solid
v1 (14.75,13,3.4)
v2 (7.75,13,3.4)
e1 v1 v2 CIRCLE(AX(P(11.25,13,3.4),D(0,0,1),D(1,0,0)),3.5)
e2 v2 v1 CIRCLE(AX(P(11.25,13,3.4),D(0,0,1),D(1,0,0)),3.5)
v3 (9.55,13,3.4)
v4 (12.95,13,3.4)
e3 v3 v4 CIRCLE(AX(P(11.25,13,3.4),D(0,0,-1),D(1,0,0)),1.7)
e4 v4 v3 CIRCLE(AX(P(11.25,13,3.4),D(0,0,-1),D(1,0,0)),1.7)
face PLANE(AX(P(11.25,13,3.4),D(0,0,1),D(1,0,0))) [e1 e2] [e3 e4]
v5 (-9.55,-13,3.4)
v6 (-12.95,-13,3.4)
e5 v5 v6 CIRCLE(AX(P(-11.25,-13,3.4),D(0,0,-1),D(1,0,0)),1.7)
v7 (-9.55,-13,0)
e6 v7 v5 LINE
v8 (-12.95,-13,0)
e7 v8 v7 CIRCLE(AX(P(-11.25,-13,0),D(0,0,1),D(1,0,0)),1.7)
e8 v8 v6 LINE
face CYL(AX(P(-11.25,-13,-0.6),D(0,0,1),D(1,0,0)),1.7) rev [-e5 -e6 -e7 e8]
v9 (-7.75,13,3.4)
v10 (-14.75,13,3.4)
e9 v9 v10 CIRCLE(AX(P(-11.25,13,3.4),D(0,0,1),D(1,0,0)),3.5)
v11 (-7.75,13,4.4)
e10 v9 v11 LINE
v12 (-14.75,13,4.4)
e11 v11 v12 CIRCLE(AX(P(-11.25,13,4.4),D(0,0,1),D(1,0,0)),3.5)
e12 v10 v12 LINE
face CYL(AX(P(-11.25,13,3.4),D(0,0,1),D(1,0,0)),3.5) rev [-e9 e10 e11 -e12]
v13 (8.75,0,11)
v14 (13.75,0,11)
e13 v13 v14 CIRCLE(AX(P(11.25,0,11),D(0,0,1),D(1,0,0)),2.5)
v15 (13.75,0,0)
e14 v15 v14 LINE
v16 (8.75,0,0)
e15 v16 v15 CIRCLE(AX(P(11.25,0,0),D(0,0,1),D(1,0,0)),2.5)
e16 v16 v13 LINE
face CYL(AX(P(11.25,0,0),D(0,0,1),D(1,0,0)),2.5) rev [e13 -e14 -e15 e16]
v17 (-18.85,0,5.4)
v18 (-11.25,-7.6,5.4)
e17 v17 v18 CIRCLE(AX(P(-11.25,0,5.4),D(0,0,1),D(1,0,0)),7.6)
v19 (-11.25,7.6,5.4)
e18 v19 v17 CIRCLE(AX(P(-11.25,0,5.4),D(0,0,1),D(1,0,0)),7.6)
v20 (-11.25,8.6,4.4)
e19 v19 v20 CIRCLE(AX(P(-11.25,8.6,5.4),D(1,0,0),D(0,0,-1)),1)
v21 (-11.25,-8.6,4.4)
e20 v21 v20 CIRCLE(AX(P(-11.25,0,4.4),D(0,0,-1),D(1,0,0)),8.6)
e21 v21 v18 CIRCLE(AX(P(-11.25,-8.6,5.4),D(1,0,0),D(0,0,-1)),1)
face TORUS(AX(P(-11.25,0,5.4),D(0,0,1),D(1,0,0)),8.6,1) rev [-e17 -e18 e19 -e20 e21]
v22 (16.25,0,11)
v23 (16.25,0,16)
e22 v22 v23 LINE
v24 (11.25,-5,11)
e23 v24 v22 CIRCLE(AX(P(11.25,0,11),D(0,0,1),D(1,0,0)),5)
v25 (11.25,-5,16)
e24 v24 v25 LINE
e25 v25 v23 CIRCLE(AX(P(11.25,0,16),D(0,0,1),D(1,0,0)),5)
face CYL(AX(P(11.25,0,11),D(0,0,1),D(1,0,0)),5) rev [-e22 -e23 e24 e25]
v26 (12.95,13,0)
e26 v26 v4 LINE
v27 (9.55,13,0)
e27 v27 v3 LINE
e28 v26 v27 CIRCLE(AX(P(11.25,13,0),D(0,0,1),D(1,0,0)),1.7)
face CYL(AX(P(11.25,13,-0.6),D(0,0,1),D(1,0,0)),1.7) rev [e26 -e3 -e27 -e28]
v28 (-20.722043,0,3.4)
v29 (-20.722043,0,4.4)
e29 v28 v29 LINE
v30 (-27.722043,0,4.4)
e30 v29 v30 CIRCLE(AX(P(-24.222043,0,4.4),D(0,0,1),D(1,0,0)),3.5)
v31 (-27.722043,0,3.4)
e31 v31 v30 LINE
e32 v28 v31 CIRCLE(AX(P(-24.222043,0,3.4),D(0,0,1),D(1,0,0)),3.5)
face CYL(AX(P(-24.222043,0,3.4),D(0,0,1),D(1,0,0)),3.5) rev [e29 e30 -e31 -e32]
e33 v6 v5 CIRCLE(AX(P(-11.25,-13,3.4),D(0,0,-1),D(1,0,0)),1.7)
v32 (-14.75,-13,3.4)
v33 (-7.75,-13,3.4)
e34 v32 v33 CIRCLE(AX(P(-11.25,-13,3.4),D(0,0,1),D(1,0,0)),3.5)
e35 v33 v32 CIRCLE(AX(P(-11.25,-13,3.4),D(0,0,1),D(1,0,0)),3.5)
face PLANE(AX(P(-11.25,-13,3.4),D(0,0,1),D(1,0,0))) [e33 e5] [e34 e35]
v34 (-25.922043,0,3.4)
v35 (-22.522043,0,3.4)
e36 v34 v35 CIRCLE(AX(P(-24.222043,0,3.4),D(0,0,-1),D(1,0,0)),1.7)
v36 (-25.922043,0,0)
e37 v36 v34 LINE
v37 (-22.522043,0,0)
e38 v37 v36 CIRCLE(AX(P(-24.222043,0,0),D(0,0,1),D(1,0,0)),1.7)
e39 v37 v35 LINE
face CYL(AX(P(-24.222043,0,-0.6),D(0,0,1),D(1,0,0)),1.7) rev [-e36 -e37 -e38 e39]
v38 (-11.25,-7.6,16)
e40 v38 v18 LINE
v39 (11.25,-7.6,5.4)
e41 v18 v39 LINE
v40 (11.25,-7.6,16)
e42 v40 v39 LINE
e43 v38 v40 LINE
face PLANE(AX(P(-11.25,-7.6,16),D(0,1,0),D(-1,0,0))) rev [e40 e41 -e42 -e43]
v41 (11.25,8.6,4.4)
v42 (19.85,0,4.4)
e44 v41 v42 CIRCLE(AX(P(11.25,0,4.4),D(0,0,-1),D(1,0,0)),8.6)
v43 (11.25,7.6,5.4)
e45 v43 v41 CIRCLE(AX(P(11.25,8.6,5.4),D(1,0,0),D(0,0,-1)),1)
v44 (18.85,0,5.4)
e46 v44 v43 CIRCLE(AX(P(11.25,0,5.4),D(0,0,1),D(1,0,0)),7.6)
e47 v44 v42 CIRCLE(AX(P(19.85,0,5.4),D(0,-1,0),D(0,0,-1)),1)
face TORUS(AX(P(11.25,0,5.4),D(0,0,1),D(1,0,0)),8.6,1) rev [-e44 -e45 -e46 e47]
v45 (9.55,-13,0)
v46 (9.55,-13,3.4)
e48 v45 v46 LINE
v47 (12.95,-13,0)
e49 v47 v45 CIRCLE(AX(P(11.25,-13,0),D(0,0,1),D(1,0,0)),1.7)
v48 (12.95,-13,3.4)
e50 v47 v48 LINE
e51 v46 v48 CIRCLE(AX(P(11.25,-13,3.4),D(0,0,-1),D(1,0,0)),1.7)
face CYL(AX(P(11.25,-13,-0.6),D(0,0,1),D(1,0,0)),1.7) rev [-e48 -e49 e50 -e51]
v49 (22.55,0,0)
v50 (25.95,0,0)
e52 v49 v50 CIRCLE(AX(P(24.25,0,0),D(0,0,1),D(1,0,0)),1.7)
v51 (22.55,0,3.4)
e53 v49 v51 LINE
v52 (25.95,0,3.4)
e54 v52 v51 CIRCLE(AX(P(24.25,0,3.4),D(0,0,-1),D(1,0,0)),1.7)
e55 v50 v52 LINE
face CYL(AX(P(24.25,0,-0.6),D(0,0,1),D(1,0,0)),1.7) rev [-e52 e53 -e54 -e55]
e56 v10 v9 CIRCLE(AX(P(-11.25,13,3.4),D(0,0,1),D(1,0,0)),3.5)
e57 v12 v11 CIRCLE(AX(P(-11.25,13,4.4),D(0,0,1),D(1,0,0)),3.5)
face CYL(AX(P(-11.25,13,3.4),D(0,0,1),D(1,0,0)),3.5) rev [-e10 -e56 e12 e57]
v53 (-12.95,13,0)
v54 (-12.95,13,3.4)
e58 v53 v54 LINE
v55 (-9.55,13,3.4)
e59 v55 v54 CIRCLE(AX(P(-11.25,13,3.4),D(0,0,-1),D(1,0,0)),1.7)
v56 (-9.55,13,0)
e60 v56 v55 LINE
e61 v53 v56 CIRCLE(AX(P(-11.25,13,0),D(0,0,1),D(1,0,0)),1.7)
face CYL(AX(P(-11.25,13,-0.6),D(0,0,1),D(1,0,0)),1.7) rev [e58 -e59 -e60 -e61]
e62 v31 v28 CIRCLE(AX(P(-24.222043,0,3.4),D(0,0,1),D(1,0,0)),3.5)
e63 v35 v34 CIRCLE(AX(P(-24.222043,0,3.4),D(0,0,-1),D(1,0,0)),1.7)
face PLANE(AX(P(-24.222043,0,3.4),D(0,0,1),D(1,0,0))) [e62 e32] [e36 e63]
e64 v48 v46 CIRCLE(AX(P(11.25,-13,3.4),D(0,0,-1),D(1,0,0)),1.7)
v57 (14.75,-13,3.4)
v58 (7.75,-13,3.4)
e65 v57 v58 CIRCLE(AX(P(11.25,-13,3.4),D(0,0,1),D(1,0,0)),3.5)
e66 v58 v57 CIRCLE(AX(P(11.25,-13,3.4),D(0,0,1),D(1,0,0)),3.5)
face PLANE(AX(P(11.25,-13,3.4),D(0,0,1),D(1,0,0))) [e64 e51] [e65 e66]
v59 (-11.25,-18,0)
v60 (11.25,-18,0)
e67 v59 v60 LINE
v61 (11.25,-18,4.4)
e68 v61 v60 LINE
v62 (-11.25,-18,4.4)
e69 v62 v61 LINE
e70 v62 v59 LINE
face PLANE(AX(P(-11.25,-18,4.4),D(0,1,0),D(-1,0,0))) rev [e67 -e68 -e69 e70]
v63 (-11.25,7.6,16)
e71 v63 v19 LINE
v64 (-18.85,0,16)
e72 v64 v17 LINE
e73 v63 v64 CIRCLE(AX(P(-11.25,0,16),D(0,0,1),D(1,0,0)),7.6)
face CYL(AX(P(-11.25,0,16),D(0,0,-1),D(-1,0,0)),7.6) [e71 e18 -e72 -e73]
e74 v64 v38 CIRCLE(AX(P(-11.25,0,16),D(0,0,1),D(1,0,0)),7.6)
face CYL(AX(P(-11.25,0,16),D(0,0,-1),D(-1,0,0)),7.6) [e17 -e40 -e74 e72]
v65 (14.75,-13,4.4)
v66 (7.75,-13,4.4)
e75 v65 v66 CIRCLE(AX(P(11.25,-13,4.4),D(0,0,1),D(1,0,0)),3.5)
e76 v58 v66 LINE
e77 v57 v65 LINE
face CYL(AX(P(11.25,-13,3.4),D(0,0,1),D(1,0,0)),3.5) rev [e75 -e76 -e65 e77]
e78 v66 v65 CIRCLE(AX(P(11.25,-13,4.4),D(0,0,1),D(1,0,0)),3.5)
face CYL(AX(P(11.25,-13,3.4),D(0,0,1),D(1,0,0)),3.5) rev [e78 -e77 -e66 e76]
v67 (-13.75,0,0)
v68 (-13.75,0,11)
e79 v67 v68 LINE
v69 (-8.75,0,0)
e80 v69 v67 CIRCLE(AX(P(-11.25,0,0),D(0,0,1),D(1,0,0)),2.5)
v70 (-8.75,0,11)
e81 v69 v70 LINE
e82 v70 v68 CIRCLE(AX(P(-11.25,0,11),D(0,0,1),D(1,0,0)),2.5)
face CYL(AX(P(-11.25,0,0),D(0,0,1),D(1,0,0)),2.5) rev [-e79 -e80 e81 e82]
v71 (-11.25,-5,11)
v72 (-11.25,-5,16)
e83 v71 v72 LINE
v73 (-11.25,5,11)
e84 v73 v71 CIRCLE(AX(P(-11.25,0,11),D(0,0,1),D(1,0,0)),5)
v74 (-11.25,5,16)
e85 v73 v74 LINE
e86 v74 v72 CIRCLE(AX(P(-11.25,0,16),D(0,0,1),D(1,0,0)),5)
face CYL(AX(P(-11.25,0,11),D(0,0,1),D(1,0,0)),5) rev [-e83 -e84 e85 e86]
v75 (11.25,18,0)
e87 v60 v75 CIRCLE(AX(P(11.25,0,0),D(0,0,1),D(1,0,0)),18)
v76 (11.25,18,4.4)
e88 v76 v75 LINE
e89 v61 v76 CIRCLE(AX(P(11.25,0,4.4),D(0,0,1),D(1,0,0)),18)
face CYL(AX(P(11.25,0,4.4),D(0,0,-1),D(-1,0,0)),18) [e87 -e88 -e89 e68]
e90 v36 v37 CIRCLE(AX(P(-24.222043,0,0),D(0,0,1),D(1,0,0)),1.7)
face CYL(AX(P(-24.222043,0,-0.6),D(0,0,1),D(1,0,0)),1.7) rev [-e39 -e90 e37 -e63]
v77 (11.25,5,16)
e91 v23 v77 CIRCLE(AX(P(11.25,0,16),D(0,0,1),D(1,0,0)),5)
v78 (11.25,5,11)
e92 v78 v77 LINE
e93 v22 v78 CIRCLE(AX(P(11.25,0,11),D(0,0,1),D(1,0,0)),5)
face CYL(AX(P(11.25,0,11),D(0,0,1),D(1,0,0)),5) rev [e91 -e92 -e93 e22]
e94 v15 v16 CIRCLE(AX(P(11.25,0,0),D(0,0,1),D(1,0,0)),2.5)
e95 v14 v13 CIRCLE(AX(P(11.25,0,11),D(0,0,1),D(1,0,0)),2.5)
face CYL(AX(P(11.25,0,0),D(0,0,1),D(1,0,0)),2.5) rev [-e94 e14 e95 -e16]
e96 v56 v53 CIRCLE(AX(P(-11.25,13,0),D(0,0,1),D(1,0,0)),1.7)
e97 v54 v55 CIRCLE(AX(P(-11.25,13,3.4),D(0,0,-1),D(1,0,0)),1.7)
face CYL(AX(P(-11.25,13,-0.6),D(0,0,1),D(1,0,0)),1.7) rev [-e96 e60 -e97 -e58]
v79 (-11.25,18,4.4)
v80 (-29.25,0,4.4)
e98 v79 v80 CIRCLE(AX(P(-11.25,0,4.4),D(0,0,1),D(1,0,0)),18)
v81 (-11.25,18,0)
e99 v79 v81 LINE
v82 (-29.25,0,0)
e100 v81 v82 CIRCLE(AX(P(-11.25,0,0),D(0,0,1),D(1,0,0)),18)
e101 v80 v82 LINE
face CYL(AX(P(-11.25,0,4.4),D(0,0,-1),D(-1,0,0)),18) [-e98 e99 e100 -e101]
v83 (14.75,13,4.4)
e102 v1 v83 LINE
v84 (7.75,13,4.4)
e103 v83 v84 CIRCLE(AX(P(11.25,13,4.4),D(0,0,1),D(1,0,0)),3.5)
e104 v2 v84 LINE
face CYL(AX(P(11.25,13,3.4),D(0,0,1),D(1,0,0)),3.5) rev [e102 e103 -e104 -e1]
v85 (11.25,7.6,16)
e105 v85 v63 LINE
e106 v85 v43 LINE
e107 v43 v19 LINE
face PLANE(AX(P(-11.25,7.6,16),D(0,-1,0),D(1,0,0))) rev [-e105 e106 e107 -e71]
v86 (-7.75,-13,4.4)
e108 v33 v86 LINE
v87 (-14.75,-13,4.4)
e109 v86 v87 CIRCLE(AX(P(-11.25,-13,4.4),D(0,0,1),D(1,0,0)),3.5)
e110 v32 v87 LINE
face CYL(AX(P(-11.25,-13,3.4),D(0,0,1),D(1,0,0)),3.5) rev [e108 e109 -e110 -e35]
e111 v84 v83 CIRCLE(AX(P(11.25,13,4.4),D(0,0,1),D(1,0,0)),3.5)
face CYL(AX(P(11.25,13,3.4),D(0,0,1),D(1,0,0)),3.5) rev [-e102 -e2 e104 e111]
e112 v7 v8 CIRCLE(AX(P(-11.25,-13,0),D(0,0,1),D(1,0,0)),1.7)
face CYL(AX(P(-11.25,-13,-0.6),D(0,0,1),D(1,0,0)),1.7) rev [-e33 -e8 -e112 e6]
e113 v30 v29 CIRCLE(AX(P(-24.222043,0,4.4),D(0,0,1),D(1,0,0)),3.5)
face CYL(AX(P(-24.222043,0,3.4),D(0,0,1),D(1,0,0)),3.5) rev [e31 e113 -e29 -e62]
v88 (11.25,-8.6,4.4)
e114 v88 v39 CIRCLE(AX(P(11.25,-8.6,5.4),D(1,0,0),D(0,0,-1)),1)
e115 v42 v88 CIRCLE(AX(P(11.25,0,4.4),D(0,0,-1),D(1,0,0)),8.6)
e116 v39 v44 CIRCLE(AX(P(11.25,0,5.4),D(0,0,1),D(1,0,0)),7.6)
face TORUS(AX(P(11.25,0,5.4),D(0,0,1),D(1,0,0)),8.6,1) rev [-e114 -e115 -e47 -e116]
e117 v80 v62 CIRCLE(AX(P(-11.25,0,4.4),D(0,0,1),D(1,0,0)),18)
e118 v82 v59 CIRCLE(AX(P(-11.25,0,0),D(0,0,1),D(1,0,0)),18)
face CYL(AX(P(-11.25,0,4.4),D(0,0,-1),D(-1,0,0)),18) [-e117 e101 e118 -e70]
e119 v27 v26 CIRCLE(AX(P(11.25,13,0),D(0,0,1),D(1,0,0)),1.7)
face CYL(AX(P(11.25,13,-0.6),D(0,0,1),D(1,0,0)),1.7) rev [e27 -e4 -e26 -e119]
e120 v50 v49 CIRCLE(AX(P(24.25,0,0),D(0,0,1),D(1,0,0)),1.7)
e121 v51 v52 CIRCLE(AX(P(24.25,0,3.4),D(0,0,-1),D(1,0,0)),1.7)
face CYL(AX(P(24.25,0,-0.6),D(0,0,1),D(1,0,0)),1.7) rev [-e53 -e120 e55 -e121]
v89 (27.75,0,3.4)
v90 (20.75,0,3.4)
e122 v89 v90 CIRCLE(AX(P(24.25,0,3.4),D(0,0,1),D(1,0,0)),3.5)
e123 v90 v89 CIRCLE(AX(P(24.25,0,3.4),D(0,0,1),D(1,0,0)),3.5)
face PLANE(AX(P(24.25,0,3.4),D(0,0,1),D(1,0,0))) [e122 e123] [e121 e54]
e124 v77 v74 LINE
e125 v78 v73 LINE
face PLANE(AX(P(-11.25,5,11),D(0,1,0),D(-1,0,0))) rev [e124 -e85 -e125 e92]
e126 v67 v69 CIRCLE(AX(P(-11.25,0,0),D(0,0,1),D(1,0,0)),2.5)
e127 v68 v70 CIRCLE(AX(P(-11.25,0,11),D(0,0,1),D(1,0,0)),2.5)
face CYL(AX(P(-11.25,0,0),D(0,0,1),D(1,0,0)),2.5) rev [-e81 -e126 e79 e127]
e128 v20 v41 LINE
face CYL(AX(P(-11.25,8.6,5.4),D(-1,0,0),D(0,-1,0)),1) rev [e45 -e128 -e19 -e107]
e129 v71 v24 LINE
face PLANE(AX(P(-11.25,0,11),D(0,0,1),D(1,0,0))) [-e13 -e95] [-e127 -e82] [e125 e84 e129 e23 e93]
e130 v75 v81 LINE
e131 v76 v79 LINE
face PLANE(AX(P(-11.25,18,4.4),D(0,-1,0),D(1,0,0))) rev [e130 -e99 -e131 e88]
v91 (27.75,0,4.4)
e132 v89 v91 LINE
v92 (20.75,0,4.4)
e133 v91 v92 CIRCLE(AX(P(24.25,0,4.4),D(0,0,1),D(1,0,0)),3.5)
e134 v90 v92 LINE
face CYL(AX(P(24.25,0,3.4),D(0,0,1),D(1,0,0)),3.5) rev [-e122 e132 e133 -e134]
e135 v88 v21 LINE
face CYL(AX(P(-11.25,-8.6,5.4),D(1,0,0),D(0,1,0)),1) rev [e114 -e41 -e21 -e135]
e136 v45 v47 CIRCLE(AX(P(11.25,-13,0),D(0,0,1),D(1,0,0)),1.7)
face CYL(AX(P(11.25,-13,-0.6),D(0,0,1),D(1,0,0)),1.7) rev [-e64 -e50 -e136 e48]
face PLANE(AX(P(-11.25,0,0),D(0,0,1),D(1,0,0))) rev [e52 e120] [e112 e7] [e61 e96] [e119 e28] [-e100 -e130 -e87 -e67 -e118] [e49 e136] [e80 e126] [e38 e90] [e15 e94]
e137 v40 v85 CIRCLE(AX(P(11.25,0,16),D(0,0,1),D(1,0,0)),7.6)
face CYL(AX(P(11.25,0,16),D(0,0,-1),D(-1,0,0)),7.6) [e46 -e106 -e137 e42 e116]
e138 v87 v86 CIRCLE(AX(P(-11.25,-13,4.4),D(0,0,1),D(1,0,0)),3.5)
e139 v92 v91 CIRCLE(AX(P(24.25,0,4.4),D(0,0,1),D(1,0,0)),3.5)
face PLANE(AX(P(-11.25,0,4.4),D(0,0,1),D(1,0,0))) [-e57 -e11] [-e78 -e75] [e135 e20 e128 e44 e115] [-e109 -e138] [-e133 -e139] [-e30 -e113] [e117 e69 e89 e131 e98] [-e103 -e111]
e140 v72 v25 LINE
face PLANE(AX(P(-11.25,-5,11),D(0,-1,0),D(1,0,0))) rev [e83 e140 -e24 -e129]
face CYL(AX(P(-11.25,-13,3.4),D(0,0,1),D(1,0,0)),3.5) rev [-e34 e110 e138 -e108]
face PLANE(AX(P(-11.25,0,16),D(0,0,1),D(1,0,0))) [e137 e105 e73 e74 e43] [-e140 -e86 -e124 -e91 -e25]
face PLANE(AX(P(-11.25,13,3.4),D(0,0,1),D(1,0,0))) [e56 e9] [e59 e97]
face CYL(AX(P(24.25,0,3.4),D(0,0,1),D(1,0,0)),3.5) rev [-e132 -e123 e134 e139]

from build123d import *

# Parameters (mm, degrees)
OVAL_BASE_FLANGE_DEPTH       = 4.4
RAISED_OBROUND_HOUSING_DEPTH = 11.6
HOUSING_SLOT_R5_DEPTH        = 5
MOUNTING_HOLES_SKETCH_R      = 1.7
MOUNTING_HOLES_6X_3_4_DEPTH  = 5
COUNTERBORE_SKETCH_R         = 3.5
COUNTERBORES_6X_7_DEPTH      = 1
SLOT_THROUGH_CUT_SKETCH_R    = 2.5
SLOT_THROUGH_CUT_DEPTH       = 37.063312383
HOUSING_BASE_FILLET_R1_R     = 1


with BuildPart() as part:
    # Flange Profile Sketch → Oval Base Flange (new body)
    with BuildSketch(Plane.XY):
        with BuildLine():
            Line((-11.25, 18), (11.25, 18))
            ThreePointArc((11.25, 18), (29.25, 0), (11.25, -18))
            Line((11.25, -18), (-11.25, -18))
            ThreePointArc((-11.25, -18), (-29.25, 0), (-11.25, 18))
        make_face()
    extrude(amount=OVAL_BASE_FLANGE_DEPTH)

    # Housing Profile Sketch → Raised Obround Housing (add)
    with BuildSketch(Plane.XY.offset(4.4)):
        with BuildLine():
            Line((-11.25, 7.6), (11.25, 7.6))
            ThreePointArc((11.25, 7.6), (18.85, 0), (11.25, -7.6))
            Line((11.25, -7.6), (-11.25, -7.6))
            ThreePointArc((-11.25, -7.6), (-18.85, 0), (-11.25, 7.6))
        make_face()
    extrude(amount=RAISED_OBROUND_HOUSING_DEPTH)

    # Housing Slot Sketch → Housing Slot R5 (cut)
    with BuildSketch(Plane.XY.offset(16)):
        with BuildLine():
            Line((-11.25, 5), (11.25, 5))
            ThreePointArc((11.25, 5), (16.25, 0), (11.25, -5))
            Line((11.25, -5), (-11.25, -5))
            ThreePointArc((-11.25, -5), (-16.25, 0), (-11.25, 5))
        make_face()
    extrude(amount=-HOUSING_SLOT_R5_DEPTH, mode=Mode.SUBTRACT)

    # Mounting Holes Sketch → Mounting Holes 6xØ3.4 (cut)
    with BuildSketch(Plane.XY.offset(4.4)):
        with Locations((-24.22204296, 0)):
            Circle(MOUNTING_HOLES_SKETCH_R)
        with Locations((-11.25, 13)):
            Circle(MOUNTING_HOLES_SKETCH_R)
        with Locations((11.25, 13)):
            Circle(MOUNTING_HOLES_SKETCH_R)
        with Locations((24.25, 0)):
            Circle(MOUNTING_HOLES_SKETCH_R)
        with Locations((11.25, -13)):
            Circle(MOUNTING_HOLES_SKETCH_R)
        with Locations((-11.25, -13)):
            Circle(MOUNTING_HOLES_SKETCH_R)
    extrude(amount=-MOUNTING_HOLES_6X_3_4_DEPTH, mode=Mode.SUBTRACT)

    # Counterbore Sketch → Counterbores 6xØ7 (cut)
    with BuildSketch(Plane.XY.offset(4.4)):
        with Locations((-24.22204296, 0)):
            Circle(COUNTERBORE_SKETCH_R)
        with Locations((-11.25, 13)):
            Circle(COUNTERBORE_SKETCH_R)
        with Locations((11.25, 13)):
            Circle(COUNTERBORE_SKETCH_R)
        with Locations((24.25, 0)):
            Circle(COUNTERBORE_SKETCH_R)
        with Locations((11.25, -13)):
            Circle(COUNTERBORE_SKETCH_R)
        with Locations((-11.25, -13)):
            Circle(COUNTERBORE_SKETCH_R)
    extrude(amount=-COUNTERBORES_6X_7_DEPTH, mode=Mode.SUBTRACT)

    # Slot Through Cut Sketch → Slot Through Cut (cut, through all)
    with BuildSketch(Plane.XY.offset(11)):
        with Locations((-11.25, 0)):
            Circle(SLOT_THROUGH_CUT_SKETCH_R)
        with Locations((11.25, 0)):
            Circle(SLOT_THROUGH_CUT_SKETCH_R)
    extrude(amount=-SLOT_THROUGH_CUT_DEPTH, mode=Mode.SUBTRACT)

    # Housing Base Fillet R1
    housing_base_fillet_r1_edges = [part.edges().sort_by_distance(p)[0] for p in [
        (-18.85, 0, 4.4),
        (0, -7.6, 4.4),
        (18.85, 0, 4.4),
        (0, 7.6, 4.4),
    ]]
    fillet(housing_base_fillet_r1_edges, radius=HOUSING_BASE_FILLET_R1_R)


solid = part.part
